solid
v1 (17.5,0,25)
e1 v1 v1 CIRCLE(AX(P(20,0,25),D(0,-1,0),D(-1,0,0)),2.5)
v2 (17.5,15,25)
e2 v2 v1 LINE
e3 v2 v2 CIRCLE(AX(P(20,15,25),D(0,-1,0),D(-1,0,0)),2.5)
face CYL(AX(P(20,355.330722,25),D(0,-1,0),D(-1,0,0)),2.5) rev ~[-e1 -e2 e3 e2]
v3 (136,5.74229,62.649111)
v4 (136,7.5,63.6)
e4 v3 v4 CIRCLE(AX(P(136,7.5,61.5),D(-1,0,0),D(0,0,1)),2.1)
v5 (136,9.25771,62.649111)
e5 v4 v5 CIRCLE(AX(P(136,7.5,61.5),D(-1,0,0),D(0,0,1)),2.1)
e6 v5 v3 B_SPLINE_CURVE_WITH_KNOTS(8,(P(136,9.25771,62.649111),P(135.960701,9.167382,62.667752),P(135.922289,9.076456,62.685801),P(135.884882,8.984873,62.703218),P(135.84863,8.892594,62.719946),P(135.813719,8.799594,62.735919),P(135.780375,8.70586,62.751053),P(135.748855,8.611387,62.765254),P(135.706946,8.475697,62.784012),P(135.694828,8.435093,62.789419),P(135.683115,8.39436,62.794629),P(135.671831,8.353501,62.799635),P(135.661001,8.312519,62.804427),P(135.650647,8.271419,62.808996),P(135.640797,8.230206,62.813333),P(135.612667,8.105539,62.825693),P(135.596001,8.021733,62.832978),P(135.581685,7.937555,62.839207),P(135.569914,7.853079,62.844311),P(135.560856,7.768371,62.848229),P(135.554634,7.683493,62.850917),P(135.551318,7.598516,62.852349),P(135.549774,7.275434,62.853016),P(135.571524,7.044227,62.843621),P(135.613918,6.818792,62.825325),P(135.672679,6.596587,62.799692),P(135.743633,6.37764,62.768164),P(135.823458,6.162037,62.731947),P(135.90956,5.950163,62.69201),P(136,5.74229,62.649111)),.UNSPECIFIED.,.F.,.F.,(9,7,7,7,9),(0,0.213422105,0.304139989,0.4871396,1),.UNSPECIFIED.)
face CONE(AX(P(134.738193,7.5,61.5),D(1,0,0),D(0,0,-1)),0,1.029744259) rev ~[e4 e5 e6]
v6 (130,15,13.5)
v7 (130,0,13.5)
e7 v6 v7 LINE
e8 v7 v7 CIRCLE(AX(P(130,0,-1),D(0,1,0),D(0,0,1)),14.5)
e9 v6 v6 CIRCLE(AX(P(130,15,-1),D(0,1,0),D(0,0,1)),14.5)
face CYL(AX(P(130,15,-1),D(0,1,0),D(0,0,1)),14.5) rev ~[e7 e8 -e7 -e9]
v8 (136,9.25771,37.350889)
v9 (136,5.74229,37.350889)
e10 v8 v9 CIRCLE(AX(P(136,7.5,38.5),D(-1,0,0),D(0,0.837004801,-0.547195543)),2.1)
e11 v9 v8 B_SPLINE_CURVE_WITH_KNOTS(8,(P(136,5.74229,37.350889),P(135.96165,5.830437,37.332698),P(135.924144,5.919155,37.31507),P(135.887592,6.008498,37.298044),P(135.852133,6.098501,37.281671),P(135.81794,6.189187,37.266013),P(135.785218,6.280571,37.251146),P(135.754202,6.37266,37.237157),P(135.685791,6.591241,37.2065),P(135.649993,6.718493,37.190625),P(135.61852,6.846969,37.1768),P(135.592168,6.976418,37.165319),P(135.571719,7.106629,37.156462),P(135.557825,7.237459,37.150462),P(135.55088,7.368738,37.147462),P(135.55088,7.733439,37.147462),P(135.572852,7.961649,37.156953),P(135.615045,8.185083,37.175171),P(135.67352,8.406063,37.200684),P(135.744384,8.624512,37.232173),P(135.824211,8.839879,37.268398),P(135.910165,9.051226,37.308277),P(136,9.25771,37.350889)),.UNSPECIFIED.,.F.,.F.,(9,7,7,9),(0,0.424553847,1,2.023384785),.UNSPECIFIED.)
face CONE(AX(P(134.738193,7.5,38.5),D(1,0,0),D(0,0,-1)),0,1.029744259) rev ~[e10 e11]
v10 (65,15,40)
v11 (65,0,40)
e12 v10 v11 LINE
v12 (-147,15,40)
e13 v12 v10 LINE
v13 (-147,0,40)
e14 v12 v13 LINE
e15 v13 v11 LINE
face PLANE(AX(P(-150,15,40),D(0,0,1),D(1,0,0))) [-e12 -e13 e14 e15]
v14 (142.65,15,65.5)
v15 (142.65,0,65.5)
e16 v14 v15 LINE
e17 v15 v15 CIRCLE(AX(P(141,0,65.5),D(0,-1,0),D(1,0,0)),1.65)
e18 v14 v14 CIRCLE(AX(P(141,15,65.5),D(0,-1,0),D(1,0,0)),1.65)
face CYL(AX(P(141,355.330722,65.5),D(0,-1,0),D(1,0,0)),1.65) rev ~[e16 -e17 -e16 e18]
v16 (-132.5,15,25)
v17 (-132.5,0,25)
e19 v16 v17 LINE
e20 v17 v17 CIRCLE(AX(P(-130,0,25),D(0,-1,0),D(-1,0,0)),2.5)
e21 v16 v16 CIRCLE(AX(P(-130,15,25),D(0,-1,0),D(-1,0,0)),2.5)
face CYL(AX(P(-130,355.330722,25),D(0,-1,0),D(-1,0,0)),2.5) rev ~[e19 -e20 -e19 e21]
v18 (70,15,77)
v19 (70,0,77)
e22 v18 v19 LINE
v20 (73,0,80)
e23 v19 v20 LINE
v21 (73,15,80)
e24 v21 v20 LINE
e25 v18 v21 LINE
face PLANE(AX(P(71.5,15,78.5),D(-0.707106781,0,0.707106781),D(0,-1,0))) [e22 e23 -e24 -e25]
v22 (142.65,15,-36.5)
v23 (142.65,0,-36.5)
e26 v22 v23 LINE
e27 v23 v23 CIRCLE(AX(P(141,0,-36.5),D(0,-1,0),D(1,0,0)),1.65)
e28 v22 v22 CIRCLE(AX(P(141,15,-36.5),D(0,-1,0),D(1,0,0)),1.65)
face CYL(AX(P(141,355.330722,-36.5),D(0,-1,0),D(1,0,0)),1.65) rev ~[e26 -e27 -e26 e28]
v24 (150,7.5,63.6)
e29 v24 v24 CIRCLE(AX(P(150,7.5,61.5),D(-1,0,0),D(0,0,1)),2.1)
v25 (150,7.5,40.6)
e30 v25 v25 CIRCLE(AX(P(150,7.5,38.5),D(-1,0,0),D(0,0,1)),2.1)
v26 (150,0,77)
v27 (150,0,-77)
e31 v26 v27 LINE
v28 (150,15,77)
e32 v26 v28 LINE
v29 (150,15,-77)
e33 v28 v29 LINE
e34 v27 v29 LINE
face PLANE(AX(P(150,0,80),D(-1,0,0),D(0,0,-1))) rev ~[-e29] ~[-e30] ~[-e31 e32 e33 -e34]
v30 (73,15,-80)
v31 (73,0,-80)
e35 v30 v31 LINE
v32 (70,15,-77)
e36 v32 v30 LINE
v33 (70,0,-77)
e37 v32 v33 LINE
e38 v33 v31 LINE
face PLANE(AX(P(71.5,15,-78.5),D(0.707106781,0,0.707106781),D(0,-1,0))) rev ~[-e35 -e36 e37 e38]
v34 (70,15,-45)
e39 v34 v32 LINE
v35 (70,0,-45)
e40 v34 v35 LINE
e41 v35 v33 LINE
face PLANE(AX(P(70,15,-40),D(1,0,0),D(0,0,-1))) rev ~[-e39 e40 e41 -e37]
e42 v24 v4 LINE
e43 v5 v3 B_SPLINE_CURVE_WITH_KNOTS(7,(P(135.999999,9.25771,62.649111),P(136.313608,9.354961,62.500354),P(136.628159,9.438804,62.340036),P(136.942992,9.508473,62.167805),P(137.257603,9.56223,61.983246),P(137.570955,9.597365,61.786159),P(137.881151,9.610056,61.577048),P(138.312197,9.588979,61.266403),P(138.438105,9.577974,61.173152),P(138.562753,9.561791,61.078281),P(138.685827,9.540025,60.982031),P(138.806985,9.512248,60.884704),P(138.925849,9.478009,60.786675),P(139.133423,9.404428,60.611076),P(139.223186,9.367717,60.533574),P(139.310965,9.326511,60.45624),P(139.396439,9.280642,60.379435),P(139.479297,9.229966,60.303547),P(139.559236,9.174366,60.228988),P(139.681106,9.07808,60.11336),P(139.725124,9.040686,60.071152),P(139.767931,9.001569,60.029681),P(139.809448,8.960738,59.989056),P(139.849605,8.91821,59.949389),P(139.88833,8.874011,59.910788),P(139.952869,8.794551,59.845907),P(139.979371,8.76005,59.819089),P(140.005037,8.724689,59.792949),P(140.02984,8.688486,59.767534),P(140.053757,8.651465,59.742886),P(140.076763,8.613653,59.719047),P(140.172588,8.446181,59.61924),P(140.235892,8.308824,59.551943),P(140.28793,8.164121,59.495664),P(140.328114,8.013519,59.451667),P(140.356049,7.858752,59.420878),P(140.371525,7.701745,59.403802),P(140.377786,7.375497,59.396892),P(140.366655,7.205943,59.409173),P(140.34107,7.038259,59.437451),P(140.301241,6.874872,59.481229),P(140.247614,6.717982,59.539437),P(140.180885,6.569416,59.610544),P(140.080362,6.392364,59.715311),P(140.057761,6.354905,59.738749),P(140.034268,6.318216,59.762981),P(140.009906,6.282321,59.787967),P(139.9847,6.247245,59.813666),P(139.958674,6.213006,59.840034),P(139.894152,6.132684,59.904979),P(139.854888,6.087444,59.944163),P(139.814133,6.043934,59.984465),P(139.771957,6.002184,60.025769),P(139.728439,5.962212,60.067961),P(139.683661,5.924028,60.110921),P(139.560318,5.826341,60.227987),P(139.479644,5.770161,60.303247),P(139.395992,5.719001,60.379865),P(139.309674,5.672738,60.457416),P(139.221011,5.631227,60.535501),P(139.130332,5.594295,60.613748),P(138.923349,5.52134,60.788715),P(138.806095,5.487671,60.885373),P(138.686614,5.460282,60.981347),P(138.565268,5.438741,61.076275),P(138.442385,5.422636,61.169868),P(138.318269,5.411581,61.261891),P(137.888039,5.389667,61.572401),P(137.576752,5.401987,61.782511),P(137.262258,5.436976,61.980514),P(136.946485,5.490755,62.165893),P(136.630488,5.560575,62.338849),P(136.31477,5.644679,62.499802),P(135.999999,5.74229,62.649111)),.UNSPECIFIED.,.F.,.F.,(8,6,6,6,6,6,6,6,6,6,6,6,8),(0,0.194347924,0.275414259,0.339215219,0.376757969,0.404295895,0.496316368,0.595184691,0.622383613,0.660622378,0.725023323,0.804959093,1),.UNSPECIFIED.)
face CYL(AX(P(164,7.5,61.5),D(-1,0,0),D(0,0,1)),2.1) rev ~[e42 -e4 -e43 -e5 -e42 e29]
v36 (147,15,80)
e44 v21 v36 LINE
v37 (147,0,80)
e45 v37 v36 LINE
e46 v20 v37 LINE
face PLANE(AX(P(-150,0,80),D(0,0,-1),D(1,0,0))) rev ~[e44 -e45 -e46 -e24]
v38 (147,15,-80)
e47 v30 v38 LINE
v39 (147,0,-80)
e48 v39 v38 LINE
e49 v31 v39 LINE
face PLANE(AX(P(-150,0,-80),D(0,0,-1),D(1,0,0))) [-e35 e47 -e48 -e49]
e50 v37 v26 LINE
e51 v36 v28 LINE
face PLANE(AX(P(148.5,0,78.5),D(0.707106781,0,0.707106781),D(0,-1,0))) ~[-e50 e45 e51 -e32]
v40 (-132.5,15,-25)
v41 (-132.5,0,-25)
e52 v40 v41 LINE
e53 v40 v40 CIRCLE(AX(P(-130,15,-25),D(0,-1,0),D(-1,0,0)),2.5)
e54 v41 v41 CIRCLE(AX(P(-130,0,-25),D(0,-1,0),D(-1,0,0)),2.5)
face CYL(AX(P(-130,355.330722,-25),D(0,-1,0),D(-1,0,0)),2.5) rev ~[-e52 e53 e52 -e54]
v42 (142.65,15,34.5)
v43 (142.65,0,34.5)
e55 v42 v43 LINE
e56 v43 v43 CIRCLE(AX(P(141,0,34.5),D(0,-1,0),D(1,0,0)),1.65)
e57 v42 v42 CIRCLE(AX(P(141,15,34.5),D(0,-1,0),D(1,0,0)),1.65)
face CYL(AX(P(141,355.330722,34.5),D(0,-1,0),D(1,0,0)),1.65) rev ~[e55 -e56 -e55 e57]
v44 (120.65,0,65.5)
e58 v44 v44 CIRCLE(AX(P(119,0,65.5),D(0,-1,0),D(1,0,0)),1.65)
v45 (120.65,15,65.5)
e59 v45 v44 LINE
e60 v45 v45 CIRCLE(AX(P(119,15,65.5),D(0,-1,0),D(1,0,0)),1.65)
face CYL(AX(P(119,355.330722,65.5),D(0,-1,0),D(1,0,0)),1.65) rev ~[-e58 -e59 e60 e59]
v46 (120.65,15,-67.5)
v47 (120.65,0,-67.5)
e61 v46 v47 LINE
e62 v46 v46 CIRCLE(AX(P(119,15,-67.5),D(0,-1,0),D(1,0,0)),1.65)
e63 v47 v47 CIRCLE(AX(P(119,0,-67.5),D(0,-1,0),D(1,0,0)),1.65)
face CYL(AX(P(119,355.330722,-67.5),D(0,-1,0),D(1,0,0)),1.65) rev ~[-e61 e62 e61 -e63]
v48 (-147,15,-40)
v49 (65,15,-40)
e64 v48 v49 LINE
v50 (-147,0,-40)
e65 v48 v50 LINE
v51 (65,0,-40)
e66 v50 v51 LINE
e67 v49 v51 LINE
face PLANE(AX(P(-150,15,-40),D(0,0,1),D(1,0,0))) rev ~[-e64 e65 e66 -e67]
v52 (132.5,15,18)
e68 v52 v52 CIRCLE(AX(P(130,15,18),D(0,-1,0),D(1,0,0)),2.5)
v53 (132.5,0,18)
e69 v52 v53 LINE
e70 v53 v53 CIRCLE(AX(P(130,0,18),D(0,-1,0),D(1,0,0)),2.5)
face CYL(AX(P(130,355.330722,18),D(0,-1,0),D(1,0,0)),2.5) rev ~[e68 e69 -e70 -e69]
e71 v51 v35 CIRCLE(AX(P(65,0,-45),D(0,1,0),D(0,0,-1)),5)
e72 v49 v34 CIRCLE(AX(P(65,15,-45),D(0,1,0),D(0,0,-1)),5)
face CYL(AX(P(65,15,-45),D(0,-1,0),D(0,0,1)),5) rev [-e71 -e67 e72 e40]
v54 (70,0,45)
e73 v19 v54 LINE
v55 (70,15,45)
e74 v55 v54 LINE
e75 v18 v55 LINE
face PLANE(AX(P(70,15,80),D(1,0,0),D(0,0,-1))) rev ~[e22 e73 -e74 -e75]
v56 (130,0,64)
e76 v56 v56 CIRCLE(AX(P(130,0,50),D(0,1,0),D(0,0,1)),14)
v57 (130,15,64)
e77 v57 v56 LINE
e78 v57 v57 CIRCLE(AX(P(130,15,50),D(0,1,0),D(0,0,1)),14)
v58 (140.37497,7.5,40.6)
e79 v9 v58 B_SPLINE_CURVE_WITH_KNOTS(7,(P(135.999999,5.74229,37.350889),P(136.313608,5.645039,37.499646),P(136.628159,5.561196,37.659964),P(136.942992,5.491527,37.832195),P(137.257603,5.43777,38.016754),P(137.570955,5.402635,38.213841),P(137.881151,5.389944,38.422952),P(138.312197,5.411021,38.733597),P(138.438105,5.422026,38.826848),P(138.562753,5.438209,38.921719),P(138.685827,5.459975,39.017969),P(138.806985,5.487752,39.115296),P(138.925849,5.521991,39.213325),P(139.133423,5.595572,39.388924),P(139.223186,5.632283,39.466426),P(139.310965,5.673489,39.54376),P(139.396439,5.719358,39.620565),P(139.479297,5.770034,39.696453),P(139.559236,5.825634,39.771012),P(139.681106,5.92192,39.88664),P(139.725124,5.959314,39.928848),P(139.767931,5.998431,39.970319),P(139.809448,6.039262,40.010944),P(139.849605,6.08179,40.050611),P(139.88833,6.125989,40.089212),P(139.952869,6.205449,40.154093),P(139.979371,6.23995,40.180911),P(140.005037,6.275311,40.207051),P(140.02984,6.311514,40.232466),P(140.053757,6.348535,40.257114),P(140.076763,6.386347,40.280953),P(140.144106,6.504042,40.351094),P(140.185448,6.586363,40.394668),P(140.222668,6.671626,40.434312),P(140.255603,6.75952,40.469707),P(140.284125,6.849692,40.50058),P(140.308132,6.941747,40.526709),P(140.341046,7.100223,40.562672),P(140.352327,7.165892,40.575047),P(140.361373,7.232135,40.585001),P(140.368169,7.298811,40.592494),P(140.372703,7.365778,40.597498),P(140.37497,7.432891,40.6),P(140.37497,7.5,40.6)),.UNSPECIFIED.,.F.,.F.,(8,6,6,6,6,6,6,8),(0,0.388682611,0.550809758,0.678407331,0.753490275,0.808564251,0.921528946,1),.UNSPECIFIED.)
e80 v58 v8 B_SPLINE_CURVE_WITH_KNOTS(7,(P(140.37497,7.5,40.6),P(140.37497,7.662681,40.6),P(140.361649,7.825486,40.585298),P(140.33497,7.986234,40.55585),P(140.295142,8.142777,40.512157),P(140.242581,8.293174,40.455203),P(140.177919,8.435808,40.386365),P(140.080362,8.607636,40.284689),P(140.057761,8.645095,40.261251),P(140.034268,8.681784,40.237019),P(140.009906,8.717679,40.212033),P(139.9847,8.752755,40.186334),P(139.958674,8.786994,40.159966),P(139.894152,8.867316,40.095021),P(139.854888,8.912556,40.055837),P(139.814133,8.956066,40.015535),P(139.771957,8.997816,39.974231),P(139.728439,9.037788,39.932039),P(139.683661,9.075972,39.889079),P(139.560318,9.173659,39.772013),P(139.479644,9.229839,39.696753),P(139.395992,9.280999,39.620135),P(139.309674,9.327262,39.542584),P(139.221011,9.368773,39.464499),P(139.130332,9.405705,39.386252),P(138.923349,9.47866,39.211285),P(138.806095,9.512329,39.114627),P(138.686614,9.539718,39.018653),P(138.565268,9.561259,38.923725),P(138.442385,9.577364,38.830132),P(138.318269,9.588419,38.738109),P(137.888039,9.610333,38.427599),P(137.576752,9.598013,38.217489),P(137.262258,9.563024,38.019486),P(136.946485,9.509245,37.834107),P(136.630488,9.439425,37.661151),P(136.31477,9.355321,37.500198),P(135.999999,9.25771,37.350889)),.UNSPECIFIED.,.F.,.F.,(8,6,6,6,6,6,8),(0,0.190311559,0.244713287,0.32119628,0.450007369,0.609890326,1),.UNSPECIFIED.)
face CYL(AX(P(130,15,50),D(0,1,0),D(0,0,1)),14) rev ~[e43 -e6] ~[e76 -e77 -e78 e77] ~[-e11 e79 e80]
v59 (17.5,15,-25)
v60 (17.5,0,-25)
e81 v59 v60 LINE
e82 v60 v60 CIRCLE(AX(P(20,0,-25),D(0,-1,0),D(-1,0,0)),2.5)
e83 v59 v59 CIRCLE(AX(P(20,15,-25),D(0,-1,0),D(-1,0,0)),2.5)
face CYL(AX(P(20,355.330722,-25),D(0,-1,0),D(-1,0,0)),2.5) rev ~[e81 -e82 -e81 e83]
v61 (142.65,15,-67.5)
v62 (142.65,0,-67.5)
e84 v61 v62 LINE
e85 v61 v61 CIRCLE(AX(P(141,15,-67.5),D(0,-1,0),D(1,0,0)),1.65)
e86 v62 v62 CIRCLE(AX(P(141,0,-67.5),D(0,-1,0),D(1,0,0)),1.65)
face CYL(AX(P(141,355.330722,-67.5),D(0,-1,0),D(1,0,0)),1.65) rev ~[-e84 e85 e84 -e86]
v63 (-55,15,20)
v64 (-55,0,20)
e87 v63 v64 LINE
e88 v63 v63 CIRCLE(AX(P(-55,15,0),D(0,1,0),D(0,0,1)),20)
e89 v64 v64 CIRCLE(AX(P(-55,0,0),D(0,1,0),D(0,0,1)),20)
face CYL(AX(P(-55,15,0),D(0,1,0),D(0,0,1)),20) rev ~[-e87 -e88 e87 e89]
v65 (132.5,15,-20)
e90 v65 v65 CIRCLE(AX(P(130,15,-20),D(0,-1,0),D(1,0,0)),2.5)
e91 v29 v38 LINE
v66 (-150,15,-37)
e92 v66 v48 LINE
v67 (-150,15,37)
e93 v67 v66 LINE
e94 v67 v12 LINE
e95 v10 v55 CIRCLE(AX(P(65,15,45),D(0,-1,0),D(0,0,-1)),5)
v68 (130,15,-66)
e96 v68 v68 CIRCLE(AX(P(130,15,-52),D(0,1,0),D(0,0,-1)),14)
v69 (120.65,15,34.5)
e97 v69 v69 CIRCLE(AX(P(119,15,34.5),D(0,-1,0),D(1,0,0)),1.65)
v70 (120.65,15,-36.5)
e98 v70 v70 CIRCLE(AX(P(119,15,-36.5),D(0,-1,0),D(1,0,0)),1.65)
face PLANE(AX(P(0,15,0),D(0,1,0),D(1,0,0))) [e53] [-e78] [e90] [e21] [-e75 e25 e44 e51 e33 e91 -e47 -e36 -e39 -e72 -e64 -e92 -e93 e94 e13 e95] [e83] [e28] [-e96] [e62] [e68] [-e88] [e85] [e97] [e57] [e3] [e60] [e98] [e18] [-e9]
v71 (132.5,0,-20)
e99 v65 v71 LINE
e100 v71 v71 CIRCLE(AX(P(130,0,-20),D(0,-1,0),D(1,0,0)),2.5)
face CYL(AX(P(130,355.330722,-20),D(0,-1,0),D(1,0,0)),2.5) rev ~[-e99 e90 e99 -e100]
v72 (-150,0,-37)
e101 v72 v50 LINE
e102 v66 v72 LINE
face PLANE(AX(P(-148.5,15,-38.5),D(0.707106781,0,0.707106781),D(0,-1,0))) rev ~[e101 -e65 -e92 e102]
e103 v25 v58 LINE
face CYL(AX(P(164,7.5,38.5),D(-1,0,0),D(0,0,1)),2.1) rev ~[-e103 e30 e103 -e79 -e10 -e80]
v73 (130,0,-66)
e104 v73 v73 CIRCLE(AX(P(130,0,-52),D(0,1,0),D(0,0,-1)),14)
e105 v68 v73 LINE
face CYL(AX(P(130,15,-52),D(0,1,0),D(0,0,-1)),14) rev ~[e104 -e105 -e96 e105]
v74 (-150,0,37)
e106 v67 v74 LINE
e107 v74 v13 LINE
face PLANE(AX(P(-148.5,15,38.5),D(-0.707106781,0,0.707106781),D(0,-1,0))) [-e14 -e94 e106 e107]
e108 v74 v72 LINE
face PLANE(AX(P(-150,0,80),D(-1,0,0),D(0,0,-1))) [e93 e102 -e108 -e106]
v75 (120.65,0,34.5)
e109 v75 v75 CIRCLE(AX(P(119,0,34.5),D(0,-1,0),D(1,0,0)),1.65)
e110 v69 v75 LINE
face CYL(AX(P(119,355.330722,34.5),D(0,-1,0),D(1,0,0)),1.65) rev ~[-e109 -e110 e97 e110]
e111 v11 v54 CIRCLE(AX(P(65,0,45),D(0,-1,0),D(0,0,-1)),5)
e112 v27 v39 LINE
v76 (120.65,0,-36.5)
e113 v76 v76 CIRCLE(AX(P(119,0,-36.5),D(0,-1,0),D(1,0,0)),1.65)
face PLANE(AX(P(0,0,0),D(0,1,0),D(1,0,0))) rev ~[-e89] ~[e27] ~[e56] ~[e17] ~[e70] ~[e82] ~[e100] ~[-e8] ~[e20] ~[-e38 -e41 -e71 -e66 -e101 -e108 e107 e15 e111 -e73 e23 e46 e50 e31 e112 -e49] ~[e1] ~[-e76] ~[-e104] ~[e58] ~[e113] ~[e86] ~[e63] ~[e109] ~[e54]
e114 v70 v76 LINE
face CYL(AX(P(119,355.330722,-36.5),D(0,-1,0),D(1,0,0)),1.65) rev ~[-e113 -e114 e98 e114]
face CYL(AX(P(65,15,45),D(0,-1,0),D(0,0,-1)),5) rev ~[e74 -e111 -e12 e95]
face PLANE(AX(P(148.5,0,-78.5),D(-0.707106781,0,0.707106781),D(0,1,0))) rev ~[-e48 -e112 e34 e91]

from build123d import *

# Parameters (mm, degrees)
SKETCH1_W             = 300
SKETCH1_H             = 160
BOSS_EXTRUDE1_DEPTH   = 15
CHAMFER1_SIZE         = 3
SKETCH2_R             = 14
CUT_EXTRUDE1_DEPTH    = 171.660481659
M4_TAPPED_HOLE1_D     = 3.3
SKETCH5_R             = 14.5
CUT_EXTRUDE2_DEPTH    = 171.660481659
M6_TAPPED_HOLE1_D     = 5
M5_TAPPED_HOLE2_D     = 4.2
M5_TAPPED_HOLE2_DEPTH = 14
M5_TAPPED_HOLE2_TIP   = 1.2618073
SKETCH17_W            = 220
SKETCH17_H            = 40
CUT_EXTRUDE6_DEPTH    = 171.660481755
M6_TAPPED_HOLE2_D     = 5
SKETCH20_R            = 20
CUT_EXTRUDE7_DEPTH    = 171.660481755
CHAMFER2_SIZE         = 3
FILLET1_R             = 5


with BuildPart() as part:
    # Sketch1 → Boss-Extrude1 (new body)
    with BuildSketch(Plane(origin=(0, 0, 0), x_dir=(1, 0, 0), z_dir=(0, 1, 0))):
        Rectangle(SKETCH1_W, SKETCH1_H)
    extrude(amount=BOSS_EXTRUDE1_DEPTH)

    # Chamfer1
    chamfer1_edges = [part.edges().sort_by_distance(p)[0] for p in [
        (-150, 7.5, -80),
        (150, 7.5, -80),
        (150, 7.5, 80),
        (-150, 7.5, 80),
    ]]
    chamfer(chamfer1_edges, length=CHAMFER1_SIZE)

    # Sketch2 → Cut-Extrude1 (cut, through all)
    with BuildSketch(Plane(origin=(0, 15, 0), x_dir=(1, 0, 0), z_dir=(0, 1, 0))):
        with Locations(Location((130, -50, 0), (0, 0, 270))):
            Circle(SKETCH2_R)
        with Locations(Location((130, 52, 0), (0, 0, 90))):
            Circle(SKETCH2_R)
    extrude(amount=-CUT_EXTRUDE1_DEPTH, mode=Mode.SUBTRACT)

    # M4 Tapped Hole1 (through all)
    with Locations(Plane(origin=(0, 15, 0), x_dir=(-1, 0, 0), z_dir=(0, 1, 0))):
        with Locations((-141, 34.5), (-119, -67.5), (-141, -67.5), (-119, -36.5), (-141, -36.5), (-119, 34.5), (-119, 65.5), (-141, 65.5)):
            Hole(M4_TAPPED_HOLE1_D / 2)

    # Sketch5 → Cut-Extrude2 (cut, through all)
    with BuildSketch(Plane(origin=(0, 15, 0), x_dir=(1, 0, 0), z_dir=(0, 1, 0))):
        with Locations(Location((130, 1, 0), (0, 0, 270))):
            Circle(SKETCH5_R)
    extrude(amount=-CUT_EXTRUDE2_DEPTH, mode=Mode.SUBTRACT)

    # M6 Tapped Hole1 (through all)
    with Locations(Plane(origin=(0, 15, 0), x_dir=(-1, 0, 0), z_dir=(0, 1, 0))):
        with Locations((-130, -20), (-130, 18)):
            Hole(M6_TAPPED_HOLE1_D / 2)

    # M5 Tapped Hole2
    with Locations(Plane(origin=(150, 0, 0), x_dir=(0, 0, -1), z_dir=(1, 0, 0))):
        with Locations((-38.5, 7.5), (-61.5, 7.5)):
            Hole(M5_TAPPED_HOLE2_D / 2, depth=M5_TAPPED_HOLE2_DEPTH)
            with Locations((0, 0, -(M5_TAPPED_HOLE2_DEPTH + M5_TAPPED_HOLE2_TIP / 2))):  # 118° drill point
                Cone(0, M5_TAPPED_HOLE2_D / 2, M5_TAPPED_HOLE2_TIP, mode=Mode.SUBTRACT)

    # Sketch17 → Cut-Extrude6 (cut, through all)
    with BuildSketch(Plane(origin=(0, 15, 0), x_dir=(1, 0, 0), z_dir=(0, 1, 0))):
        with Locations((-40, 60)):
            Rectangle(SKETCH17_W, SKETCH17_H)
        with Locations((-40, -60)):
            Rectangle(SKETCH17_W, SKETCH17_H)
    extrude(amount=-CUT_EXTRUDE6_DEPTH, mode=Mode.SUBTRACT)

    # M6 Tapped Hole2 (through all)
    with Locations(Plane(origin=(0, 15, 0), x_dir=(1, 0, 0), z_dir=(0, 1, 0))):
        with Locations((-130, 25), (-130, -25), (20, -25), (20, 25)):
            Hole(M6_TAPPED_HOLE2_D / 2)

    # Sketch20 → Cut-Extrude7 (cut, through all)
    with BuildSketch(Plane(origin=(0, 15, 0), x_dir=(1, 0, 0), z_dir=(0, 1, 0))):
        with Locations(Location((-55, 0, 0), (0, 0, 270))):
            Circle(SKETCH20_R)
    extrude(amount=-CUT_EXTRUDE7_DEPTH, mode=Mode.SUBTRACT)

    # Chamfer2
    chamfer2_edges = [part.edges().sort_by_distance(p)[0] for p in [
        (70, 7.5, -80),
        (-150, 7.5, -40),
        (-150, 7.5, 40),
        (70, 7.5, 80),
    ]]
    chamfer(chamfer2_edges, length=CHAMFER2_SIZE)

    # Fillet1
    fillet1_edges = [part.edges().sort_by_distance(p)[0] for p in [
        (70, 7.5, -40),
        (70, 7.5, 40),
    ]]
    fillet(fillet1_edges, radius=FILLET1_R)


solid = part.part
